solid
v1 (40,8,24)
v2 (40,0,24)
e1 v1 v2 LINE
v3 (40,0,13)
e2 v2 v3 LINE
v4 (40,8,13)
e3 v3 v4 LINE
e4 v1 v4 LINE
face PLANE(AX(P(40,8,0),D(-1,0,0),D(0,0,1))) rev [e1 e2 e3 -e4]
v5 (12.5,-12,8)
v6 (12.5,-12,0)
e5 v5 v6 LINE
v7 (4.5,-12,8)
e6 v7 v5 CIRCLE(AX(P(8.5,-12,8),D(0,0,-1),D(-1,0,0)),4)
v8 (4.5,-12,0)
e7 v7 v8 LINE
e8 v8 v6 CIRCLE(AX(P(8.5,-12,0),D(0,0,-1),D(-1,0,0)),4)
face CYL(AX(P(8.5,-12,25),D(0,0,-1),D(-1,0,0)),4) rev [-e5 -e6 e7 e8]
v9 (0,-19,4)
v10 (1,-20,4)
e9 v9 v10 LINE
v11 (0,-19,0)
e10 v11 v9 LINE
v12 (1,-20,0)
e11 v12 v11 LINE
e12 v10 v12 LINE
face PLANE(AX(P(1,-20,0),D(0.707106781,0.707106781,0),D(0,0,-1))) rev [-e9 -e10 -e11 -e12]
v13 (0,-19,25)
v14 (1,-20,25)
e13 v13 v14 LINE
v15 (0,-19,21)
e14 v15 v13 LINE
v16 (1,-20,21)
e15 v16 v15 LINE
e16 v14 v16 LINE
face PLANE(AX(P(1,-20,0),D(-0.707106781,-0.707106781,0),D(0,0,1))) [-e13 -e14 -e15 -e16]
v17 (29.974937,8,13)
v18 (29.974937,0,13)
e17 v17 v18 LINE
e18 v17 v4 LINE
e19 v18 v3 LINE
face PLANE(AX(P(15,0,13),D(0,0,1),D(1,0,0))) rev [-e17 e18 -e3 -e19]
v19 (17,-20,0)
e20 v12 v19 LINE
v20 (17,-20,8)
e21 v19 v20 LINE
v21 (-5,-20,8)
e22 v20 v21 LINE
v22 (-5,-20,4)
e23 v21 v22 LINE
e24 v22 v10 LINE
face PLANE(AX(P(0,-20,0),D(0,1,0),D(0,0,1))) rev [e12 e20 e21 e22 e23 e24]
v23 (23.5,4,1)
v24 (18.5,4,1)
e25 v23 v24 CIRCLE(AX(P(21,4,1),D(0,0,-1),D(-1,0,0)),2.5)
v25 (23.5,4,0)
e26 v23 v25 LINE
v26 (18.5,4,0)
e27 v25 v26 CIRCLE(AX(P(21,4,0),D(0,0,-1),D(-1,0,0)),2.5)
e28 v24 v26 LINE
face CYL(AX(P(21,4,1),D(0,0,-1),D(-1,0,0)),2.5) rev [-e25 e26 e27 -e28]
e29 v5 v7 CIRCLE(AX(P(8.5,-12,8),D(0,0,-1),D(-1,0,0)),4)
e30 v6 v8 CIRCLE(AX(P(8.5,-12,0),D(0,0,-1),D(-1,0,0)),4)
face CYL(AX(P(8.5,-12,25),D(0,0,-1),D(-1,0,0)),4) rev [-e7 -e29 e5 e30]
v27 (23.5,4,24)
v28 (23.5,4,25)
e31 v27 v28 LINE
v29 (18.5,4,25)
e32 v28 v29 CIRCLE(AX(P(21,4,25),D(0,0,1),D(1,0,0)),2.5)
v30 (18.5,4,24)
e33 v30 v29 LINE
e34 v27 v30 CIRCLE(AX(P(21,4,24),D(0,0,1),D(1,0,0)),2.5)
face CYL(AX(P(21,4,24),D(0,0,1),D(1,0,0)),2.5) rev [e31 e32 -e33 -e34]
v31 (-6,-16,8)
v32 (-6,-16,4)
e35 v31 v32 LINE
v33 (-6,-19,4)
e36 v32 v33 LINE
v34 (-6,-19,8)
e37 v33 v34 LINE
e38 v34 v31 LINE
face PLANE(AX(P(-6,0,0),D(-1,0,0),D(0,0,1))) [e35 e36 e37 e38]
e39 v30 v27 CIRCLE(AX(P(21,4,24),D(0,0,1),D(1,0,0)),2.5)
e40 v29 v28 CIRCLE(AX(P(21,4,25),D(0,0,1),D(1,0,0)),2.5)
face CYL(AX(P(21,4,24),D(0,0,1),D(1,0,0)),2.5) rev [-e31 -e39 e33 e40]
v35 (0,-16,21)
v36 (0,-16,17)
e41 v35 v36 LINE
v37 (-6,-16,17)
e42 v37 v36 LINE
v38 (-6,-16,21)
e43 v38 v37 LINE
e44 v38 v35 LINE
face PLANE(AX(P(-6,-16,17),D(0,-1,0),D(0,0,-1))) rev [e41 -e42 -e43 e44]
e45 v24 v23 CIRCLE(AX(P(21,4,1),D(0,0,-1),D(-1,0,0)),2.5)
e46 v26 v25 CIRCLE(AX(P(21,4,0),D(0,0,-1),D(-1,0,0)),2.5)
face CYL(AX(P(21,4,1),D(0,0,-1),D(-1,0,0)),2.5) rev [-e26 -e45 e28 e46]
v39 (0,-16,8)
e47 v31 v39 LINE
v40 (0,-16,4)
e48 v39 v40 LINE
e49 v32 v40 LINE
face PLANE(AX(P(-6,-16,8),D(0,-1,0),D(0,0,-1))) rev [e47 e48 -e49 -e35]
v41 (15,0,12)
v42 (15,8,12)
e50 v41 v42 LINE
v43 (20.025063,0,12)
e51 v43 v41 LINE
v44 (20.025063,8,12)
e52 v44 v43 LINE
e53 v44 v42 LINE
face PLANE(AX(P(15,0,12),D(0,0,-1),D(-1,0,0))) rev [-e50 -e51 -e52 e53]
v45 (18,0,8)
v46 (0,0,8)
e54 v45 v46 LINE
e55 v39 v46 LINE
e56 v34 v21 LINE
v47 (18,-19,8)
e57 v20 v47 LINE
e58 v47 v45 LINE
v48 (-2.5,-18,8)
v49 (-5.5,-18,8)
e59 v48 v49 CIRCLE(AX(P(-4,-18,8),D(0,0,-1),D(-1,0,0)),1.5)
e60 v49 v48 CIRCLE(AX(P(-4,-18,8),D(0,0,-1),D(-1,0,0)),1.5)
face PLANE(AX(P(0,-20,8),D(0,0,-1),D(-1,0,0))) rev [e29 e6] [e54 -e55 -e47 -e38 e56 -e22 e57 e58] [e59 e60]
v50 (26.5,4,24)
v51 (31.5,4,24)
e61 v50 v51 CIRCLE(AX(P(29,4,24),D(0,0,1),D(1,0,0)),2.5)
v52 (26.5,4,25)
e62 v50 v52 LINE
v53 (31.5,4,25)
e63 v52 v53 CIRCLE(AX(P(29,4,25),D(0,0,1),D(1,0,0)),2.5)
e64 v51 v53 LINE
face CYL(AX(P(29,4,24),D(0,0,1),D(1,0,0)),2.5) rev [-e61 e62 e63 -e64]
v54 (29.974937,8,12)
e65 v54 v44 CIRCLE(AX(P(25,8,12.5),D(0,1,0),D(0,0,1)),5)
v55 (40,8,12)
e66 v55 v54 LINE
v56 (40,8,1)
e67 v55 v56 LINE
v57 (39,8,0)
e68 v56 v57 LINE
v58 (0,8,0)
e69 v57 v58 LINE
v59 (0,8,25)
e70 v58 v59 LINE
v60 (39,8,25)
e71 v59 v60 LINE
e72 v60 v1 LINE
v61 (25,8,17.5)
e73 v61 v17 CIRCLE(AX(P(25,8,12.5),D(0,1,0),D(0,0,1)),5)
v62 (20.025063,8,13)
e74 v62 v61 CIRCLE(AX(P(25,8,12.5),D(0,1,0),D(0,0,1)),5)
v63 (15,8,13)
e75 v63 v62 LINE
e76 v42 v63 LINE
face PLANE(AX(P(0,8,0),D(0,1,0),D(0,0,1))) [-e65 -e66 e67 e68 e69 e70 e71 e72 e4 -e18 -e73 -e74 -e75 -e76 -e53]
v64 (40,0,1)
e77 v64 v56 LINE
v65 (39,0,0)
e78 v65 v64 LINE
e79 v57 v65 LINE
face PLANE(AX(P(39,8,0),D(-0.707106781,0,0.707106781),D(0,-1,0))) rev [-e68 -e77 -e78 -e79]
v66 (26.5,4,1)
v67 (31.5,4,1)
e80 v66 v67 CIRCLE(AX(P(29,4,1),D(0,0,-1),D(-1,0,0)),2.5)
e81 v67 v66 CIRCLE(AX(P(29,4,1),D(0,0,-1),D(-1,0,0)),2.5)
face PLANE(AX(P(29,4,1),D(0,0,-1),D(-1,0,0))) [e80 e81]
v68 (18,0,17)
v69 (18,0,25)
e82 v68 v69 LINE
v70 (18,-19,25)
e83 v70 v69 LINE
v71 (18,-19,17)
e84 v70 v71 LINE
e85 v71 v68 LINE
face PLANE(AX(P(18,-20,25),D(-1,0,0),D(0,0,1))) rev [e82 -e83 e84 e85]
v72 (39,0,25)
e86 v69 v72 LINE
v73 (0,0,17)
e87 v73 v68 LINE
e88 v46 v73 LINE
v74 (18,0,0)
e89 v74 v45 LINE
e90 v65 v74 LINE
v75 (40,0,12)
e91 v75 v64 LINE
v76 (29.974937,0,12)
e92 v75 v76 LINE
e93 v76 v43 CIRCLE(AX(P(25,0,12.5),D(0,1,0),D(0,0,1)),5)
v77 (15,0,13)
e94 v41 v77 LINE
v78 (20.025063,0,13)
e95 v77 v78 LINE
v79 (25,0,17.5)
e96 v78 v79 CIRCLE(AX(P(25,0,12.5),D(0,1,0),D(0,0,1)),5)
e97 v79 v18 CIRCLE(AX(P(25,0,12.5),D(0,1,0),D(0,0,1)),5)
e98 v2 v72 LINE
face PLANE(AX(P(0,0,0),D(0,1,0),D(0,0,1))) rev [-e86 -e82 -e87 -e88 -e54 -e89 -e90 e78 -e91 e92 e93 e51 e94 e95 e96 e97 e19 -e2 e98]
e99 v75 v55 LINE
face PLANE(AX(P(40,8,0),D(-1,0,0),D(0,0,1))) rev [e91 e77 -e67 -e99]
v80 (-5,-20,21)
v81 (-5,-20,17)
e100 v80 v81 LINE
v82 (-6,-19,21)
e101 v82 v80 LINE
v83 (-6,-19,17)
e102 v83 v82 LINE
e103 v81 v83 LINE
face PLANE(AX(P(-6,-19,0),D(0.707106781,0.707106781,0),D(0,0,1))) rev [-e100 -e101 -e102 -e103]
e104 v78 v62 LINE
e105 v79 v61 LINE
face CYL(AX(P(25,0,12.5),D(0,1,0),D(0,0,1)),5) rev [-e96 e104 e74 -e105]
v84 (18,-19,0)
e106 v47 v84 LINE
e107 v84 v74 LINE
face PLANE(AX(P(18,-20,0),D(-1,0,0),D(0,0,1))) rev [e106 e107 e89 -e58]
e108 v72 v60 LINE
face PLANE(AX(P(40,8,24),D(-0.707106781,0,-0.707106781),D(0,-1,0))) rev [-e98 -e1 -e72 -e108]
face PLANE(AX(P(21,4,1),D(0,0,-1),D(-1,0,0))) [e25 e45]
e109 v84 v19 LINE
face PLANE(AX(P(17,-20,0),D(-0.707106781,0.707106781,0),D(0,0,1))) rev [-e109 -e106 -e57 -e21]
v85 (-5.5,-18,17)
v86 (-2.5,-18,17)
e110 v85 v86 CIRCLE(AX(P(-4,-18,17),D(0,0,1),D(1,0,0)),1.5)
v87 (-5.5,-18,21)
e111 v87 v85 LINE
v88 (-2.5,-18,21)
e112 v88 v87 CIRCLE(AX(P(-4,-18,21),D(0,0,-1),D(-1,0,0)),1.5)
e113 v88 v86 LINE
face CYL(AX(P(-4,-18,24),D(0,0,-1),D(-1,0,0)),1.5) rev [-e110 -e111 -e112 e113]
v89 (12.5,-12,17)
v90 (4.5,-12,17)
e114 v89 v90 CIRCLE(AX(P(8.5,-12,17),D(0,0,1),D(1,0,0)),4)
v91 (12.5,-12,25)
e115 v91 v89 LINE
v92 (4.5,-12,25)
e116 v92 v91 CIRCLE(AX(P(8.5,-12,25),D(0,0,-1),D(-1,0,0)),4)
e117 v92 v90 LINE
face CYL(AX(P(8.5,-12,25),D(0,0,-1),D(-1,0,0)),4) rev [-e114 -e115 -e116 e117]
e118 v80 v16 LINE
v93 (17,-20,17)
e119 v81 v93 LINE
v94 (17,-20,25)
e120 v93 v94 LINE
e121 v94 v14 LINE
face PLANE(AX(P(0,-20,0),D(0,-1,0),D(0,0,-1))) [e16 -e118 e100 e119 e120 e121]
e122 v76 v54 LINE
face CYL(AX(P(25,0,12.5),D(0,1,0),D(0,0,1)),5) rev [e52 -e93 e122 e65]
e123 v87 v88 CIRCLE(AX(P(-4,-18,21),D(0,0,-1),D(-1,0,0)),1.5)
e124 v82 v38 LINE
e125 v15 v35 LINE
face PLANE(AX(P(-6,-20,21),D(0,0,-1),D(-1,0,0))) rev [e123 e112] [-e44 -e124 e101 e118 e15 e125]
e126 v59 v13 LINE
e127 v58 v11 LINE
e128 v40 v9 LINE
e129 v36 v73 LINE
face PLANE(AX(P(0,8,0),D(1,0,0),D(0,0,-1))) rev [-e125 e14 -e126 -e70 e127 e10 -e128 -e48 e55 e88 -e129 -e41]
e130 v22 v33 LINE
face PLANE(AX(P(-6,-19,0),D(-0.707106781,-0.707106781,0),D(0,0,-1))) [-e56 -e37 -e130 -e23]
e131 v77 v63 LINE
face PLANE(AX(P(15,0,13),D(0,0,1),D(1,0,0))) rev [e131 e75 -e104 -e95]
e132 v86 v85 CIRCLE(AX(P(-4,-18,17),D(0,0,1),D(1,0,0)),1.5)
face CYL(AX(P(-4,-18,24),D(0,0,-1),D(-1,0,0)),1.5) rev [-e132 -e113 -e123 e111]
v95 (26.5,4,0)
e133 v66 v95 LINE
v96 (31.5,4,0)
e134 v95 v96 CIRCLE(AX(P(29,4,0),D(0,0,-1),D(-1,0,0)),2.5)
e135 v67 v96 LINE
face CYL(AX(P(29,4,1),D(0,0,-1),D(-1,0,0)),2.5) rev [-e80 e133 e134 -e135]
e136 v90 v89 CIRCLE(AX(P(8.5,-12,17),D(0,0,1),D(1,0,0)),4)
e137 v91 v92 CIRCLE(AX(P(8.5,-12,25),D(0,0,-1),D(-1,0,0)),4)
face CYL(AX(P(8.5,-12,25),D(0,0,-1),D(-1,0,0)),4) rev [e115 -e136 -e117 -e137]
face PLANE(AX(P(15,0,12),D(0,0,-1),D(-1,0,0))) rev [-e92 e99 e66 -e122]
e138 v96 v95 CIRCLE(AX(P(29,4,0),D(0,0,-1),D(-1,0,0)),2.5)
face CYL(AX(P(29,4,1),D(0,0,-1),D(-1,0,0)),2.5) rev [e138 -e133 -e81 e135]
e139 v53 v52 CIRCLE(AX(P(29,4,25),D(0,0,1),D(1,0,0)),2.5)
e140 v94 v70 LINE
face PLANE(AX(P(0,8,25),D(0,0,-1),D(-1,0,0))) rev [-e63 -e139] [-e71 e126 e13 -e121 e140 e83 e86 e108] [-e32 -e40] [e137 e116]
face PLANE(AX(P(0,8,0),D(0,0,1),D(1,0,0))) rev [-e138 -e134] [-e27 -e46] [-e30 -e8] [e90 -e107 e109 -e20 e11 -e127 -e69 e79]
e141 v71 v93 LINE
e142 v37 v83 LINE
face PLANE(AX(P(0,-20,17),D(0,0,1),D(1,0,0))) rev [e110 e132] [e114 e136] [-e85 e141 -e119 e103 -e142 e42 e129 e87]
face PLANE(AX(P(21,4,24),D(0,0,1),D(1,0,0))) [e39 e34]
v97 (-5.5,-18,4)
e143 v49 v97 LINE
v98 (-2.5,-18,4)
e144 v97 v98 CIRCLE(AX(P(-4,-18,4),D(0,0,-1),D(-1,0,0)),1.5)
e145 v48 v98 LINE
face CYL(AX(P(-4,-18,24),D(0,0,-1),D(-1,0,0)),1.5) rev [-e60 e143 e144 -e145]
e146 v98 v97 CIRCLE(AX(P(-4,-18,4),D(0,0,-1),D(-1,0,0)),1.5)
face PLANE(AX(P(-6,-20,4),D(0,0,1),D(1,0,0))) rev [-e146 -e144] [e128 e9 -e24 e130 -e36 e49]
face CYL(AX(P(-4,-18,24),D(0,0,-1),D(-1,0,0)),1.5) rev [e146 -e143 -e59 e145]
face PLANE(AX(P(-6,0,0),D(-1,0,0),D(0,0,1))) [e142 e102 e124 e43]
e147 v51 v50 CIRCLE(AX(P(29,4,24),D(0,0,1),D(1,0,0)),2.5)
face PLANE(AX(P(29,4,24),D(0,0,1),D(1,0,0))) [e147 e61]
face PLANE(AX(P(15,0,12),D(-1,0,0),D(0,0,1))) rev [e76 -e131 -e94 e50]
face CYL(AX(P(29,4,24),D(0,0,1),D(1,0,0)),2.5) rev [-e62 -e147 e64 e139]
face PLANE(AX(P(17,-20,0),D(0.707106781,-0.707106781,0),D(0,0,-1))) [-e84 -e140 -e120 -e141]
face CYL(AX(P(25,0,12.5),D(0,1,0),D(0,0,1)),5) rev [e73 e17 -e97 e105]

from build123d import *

# Parameters (mm, degrees)
SKETCH1_W           = 40
SKETCH1_H           = 25
BOSS_EXTRUDE1_DEPTH = 8
SKETCH3_R           = 5
CUT_EXTRUDE1_DEPTH  = 48.843494856
SKETCH4_W           = 25
SKETCH4_H           = 1
CUT_EXTRUDE2_DEPTH  = 48.843494856
SKETCH7_W           = 18
SKETCH7_H           = 8
BOSS_EXTRUDE2_DEPTH = 20
CHAMFER2_SIZE       = 1
SKETCH8_R           = 4
CUT_EXTRUDE3_DEPTH  = 52.23475383
SKETCH9_R           = 2.5
CUT_EXTRUDE4_DEPTH  = 1
CUT_EXTRUDE5_START  = -1
SKETCH10_R          = 2.5
CUT_EXTRUDE5_DEPTH  = 1
SKETCH11_W          = 4
SKETCH11_H          = 4
BOSS_EXTRUDE3_DEPTH = 6
SKETCH12_R          = 1.5
CUT_EXTRUDE6_DEPTH  = 20
CHAMFER4_SIZE       = 1


with BuildPart() as part:
    # Sketch1 → Boss-Extrude1 (new body)
    with BuildSketch(Plane(origin=(0, 0, 0), x_dir=(1, 0, 0), z_dir=(0, 1, 0))):
        with Locations((20, -12.5)):
            Rectangle(SKETCH1_W, SKETCH1_H)
    extrude(amount=BOSS_EXTRUDE1_DEPTH)

    # Sketch3 → Cut-Extrude1 (cut, through all)
    with BuildSketch(Plane(origin=(0, 8, 0), x_dir=(1, 0, 0), z_dir=(0, 1, 0))):
        with Locations(Location((25, -12.5, 0), (0, 0, 270))):
            Circle(SKETCH3_R)
    extrude(amount=-CUT_EXTRUDE1_DEPTH, mode=Mode.SUBTRACT)

    # Sketch4 → Cut-Extrude2 (cut, through all)
    with BuildSketch(Plane(origin=(0, 8, 0), x_dir=(1, 0, 0), z_dir=(0, 1, 0))):
        with Locations((27.5, -12.5)):
            Rectangle(SKETCH4_W, SKETCH4_H)
    extrude(amount=-CUT_EXTRUDE2_DEPTH, mode=Mode.SUBTRACT)

    # Sketch7 → Boss-Extrude2 (add)
    with BuildSketch(Plane.XZ):
        with Locations((9, 4)):
            Rectangle(SKETCH7_W, SKETCH7_H)
        with Locations((9, 21)):
            Rectangle(SKETCH7_W, SKETCH7_H)
    extrude(amount=BOSS_EXTRUDE2_DEPTH)

    # Chamfer2
    chamfer2_edges = [part.edges().sort_by_distance(p)[0] for p in [
        (18, -20, 4),
        (18, -20, 21),
        (40, 4, 0),
        (40, 4, 25),
    ]]
    chamfer(chamfer2_edges, length=CHAMFER2_SIZE)

    # Sketch8 → Cut-Extrude3 (cut, through all)
    with BuildSketch(Plane(origin=(0, 0, 0), x_dir=(-1, 0, 0), z_dir=(0, 0, -1))):
        with Locations((-8.5, -12)):
            Circle(SKETCH8_R)
    extrude(amount=-CUT_EXTRUDE3_DEPTH, mode=Mode.SUBTRACT)

    # Sketch9 → Cut-Extrude4 (cut)
    with BuildSketch(Plane(origin=(0, 0, 0), x_dir=(-1, 0, 0), z_dir=(0, 0, -1))):
        with Locations((-29, 4)):
            Circle(SKETCH9_R)
        with Locations((-21, 4)):
            Circle(SKETCH9_R)
    extrude(amount=-CUT_EXTRUDE4_DEPTH, mode=Mode.SUBTRACT)

    # Sketch10 → Cut-Extrude5 (cut)
    with BuildSketch(Plane.XY.offset(25).offset(CUT_EXTRUDE5_START)):
        with Locations(Location((21, 4, 0), (0, 0, 180))):
            Circle(SKETCH10_R)
        with Locations(Location((29, 4, 0), (0, 0, 180))):
            Circle(SKETCH10_R)
    extrude(amount=CUT_EXTRUDE5_DEPTH, mode=Mode.SUBTRACT)

    # Sketch11 → Boss-Extrude3 (add)
    with BuildSketch(Plane.ZY):
        with Locations((19, -18)):
            Rectangle(SKETCH11_W, SKETCH11_H)
        with Locations((6, -18)):
            Rectangle(SKETCH11_W, SKETCH11_H)
    extrude(amount=BOSS_EXTRUDE3_DEPTH)

    # Sketch12 → Cut-Extrude6 (cut)
    with BuildSketch(Plane(origin=(0, 0, 4), x_dir=(-1, 0, 0), z_dir=(0, 0, -1))):
        with Locations((4, -18)):
            Circle(SKETCH12_R)
    extrude(amount=-CUT_EXTRUDE6_DEPTH, mode=Mode.SUBTRACT)

    # Chamfer4
    chamfer4_edges = [part.edges().sort_by_distance(p)[0] for p in [
        (0, -20, 2),
        (-6, -20, 6),
        (-6, -20, 19),
        (0, -20, 23),
    ]]
    chamfer(chamfer4_edges, length=CHAMFER4_SIZE)


solid = part.part
